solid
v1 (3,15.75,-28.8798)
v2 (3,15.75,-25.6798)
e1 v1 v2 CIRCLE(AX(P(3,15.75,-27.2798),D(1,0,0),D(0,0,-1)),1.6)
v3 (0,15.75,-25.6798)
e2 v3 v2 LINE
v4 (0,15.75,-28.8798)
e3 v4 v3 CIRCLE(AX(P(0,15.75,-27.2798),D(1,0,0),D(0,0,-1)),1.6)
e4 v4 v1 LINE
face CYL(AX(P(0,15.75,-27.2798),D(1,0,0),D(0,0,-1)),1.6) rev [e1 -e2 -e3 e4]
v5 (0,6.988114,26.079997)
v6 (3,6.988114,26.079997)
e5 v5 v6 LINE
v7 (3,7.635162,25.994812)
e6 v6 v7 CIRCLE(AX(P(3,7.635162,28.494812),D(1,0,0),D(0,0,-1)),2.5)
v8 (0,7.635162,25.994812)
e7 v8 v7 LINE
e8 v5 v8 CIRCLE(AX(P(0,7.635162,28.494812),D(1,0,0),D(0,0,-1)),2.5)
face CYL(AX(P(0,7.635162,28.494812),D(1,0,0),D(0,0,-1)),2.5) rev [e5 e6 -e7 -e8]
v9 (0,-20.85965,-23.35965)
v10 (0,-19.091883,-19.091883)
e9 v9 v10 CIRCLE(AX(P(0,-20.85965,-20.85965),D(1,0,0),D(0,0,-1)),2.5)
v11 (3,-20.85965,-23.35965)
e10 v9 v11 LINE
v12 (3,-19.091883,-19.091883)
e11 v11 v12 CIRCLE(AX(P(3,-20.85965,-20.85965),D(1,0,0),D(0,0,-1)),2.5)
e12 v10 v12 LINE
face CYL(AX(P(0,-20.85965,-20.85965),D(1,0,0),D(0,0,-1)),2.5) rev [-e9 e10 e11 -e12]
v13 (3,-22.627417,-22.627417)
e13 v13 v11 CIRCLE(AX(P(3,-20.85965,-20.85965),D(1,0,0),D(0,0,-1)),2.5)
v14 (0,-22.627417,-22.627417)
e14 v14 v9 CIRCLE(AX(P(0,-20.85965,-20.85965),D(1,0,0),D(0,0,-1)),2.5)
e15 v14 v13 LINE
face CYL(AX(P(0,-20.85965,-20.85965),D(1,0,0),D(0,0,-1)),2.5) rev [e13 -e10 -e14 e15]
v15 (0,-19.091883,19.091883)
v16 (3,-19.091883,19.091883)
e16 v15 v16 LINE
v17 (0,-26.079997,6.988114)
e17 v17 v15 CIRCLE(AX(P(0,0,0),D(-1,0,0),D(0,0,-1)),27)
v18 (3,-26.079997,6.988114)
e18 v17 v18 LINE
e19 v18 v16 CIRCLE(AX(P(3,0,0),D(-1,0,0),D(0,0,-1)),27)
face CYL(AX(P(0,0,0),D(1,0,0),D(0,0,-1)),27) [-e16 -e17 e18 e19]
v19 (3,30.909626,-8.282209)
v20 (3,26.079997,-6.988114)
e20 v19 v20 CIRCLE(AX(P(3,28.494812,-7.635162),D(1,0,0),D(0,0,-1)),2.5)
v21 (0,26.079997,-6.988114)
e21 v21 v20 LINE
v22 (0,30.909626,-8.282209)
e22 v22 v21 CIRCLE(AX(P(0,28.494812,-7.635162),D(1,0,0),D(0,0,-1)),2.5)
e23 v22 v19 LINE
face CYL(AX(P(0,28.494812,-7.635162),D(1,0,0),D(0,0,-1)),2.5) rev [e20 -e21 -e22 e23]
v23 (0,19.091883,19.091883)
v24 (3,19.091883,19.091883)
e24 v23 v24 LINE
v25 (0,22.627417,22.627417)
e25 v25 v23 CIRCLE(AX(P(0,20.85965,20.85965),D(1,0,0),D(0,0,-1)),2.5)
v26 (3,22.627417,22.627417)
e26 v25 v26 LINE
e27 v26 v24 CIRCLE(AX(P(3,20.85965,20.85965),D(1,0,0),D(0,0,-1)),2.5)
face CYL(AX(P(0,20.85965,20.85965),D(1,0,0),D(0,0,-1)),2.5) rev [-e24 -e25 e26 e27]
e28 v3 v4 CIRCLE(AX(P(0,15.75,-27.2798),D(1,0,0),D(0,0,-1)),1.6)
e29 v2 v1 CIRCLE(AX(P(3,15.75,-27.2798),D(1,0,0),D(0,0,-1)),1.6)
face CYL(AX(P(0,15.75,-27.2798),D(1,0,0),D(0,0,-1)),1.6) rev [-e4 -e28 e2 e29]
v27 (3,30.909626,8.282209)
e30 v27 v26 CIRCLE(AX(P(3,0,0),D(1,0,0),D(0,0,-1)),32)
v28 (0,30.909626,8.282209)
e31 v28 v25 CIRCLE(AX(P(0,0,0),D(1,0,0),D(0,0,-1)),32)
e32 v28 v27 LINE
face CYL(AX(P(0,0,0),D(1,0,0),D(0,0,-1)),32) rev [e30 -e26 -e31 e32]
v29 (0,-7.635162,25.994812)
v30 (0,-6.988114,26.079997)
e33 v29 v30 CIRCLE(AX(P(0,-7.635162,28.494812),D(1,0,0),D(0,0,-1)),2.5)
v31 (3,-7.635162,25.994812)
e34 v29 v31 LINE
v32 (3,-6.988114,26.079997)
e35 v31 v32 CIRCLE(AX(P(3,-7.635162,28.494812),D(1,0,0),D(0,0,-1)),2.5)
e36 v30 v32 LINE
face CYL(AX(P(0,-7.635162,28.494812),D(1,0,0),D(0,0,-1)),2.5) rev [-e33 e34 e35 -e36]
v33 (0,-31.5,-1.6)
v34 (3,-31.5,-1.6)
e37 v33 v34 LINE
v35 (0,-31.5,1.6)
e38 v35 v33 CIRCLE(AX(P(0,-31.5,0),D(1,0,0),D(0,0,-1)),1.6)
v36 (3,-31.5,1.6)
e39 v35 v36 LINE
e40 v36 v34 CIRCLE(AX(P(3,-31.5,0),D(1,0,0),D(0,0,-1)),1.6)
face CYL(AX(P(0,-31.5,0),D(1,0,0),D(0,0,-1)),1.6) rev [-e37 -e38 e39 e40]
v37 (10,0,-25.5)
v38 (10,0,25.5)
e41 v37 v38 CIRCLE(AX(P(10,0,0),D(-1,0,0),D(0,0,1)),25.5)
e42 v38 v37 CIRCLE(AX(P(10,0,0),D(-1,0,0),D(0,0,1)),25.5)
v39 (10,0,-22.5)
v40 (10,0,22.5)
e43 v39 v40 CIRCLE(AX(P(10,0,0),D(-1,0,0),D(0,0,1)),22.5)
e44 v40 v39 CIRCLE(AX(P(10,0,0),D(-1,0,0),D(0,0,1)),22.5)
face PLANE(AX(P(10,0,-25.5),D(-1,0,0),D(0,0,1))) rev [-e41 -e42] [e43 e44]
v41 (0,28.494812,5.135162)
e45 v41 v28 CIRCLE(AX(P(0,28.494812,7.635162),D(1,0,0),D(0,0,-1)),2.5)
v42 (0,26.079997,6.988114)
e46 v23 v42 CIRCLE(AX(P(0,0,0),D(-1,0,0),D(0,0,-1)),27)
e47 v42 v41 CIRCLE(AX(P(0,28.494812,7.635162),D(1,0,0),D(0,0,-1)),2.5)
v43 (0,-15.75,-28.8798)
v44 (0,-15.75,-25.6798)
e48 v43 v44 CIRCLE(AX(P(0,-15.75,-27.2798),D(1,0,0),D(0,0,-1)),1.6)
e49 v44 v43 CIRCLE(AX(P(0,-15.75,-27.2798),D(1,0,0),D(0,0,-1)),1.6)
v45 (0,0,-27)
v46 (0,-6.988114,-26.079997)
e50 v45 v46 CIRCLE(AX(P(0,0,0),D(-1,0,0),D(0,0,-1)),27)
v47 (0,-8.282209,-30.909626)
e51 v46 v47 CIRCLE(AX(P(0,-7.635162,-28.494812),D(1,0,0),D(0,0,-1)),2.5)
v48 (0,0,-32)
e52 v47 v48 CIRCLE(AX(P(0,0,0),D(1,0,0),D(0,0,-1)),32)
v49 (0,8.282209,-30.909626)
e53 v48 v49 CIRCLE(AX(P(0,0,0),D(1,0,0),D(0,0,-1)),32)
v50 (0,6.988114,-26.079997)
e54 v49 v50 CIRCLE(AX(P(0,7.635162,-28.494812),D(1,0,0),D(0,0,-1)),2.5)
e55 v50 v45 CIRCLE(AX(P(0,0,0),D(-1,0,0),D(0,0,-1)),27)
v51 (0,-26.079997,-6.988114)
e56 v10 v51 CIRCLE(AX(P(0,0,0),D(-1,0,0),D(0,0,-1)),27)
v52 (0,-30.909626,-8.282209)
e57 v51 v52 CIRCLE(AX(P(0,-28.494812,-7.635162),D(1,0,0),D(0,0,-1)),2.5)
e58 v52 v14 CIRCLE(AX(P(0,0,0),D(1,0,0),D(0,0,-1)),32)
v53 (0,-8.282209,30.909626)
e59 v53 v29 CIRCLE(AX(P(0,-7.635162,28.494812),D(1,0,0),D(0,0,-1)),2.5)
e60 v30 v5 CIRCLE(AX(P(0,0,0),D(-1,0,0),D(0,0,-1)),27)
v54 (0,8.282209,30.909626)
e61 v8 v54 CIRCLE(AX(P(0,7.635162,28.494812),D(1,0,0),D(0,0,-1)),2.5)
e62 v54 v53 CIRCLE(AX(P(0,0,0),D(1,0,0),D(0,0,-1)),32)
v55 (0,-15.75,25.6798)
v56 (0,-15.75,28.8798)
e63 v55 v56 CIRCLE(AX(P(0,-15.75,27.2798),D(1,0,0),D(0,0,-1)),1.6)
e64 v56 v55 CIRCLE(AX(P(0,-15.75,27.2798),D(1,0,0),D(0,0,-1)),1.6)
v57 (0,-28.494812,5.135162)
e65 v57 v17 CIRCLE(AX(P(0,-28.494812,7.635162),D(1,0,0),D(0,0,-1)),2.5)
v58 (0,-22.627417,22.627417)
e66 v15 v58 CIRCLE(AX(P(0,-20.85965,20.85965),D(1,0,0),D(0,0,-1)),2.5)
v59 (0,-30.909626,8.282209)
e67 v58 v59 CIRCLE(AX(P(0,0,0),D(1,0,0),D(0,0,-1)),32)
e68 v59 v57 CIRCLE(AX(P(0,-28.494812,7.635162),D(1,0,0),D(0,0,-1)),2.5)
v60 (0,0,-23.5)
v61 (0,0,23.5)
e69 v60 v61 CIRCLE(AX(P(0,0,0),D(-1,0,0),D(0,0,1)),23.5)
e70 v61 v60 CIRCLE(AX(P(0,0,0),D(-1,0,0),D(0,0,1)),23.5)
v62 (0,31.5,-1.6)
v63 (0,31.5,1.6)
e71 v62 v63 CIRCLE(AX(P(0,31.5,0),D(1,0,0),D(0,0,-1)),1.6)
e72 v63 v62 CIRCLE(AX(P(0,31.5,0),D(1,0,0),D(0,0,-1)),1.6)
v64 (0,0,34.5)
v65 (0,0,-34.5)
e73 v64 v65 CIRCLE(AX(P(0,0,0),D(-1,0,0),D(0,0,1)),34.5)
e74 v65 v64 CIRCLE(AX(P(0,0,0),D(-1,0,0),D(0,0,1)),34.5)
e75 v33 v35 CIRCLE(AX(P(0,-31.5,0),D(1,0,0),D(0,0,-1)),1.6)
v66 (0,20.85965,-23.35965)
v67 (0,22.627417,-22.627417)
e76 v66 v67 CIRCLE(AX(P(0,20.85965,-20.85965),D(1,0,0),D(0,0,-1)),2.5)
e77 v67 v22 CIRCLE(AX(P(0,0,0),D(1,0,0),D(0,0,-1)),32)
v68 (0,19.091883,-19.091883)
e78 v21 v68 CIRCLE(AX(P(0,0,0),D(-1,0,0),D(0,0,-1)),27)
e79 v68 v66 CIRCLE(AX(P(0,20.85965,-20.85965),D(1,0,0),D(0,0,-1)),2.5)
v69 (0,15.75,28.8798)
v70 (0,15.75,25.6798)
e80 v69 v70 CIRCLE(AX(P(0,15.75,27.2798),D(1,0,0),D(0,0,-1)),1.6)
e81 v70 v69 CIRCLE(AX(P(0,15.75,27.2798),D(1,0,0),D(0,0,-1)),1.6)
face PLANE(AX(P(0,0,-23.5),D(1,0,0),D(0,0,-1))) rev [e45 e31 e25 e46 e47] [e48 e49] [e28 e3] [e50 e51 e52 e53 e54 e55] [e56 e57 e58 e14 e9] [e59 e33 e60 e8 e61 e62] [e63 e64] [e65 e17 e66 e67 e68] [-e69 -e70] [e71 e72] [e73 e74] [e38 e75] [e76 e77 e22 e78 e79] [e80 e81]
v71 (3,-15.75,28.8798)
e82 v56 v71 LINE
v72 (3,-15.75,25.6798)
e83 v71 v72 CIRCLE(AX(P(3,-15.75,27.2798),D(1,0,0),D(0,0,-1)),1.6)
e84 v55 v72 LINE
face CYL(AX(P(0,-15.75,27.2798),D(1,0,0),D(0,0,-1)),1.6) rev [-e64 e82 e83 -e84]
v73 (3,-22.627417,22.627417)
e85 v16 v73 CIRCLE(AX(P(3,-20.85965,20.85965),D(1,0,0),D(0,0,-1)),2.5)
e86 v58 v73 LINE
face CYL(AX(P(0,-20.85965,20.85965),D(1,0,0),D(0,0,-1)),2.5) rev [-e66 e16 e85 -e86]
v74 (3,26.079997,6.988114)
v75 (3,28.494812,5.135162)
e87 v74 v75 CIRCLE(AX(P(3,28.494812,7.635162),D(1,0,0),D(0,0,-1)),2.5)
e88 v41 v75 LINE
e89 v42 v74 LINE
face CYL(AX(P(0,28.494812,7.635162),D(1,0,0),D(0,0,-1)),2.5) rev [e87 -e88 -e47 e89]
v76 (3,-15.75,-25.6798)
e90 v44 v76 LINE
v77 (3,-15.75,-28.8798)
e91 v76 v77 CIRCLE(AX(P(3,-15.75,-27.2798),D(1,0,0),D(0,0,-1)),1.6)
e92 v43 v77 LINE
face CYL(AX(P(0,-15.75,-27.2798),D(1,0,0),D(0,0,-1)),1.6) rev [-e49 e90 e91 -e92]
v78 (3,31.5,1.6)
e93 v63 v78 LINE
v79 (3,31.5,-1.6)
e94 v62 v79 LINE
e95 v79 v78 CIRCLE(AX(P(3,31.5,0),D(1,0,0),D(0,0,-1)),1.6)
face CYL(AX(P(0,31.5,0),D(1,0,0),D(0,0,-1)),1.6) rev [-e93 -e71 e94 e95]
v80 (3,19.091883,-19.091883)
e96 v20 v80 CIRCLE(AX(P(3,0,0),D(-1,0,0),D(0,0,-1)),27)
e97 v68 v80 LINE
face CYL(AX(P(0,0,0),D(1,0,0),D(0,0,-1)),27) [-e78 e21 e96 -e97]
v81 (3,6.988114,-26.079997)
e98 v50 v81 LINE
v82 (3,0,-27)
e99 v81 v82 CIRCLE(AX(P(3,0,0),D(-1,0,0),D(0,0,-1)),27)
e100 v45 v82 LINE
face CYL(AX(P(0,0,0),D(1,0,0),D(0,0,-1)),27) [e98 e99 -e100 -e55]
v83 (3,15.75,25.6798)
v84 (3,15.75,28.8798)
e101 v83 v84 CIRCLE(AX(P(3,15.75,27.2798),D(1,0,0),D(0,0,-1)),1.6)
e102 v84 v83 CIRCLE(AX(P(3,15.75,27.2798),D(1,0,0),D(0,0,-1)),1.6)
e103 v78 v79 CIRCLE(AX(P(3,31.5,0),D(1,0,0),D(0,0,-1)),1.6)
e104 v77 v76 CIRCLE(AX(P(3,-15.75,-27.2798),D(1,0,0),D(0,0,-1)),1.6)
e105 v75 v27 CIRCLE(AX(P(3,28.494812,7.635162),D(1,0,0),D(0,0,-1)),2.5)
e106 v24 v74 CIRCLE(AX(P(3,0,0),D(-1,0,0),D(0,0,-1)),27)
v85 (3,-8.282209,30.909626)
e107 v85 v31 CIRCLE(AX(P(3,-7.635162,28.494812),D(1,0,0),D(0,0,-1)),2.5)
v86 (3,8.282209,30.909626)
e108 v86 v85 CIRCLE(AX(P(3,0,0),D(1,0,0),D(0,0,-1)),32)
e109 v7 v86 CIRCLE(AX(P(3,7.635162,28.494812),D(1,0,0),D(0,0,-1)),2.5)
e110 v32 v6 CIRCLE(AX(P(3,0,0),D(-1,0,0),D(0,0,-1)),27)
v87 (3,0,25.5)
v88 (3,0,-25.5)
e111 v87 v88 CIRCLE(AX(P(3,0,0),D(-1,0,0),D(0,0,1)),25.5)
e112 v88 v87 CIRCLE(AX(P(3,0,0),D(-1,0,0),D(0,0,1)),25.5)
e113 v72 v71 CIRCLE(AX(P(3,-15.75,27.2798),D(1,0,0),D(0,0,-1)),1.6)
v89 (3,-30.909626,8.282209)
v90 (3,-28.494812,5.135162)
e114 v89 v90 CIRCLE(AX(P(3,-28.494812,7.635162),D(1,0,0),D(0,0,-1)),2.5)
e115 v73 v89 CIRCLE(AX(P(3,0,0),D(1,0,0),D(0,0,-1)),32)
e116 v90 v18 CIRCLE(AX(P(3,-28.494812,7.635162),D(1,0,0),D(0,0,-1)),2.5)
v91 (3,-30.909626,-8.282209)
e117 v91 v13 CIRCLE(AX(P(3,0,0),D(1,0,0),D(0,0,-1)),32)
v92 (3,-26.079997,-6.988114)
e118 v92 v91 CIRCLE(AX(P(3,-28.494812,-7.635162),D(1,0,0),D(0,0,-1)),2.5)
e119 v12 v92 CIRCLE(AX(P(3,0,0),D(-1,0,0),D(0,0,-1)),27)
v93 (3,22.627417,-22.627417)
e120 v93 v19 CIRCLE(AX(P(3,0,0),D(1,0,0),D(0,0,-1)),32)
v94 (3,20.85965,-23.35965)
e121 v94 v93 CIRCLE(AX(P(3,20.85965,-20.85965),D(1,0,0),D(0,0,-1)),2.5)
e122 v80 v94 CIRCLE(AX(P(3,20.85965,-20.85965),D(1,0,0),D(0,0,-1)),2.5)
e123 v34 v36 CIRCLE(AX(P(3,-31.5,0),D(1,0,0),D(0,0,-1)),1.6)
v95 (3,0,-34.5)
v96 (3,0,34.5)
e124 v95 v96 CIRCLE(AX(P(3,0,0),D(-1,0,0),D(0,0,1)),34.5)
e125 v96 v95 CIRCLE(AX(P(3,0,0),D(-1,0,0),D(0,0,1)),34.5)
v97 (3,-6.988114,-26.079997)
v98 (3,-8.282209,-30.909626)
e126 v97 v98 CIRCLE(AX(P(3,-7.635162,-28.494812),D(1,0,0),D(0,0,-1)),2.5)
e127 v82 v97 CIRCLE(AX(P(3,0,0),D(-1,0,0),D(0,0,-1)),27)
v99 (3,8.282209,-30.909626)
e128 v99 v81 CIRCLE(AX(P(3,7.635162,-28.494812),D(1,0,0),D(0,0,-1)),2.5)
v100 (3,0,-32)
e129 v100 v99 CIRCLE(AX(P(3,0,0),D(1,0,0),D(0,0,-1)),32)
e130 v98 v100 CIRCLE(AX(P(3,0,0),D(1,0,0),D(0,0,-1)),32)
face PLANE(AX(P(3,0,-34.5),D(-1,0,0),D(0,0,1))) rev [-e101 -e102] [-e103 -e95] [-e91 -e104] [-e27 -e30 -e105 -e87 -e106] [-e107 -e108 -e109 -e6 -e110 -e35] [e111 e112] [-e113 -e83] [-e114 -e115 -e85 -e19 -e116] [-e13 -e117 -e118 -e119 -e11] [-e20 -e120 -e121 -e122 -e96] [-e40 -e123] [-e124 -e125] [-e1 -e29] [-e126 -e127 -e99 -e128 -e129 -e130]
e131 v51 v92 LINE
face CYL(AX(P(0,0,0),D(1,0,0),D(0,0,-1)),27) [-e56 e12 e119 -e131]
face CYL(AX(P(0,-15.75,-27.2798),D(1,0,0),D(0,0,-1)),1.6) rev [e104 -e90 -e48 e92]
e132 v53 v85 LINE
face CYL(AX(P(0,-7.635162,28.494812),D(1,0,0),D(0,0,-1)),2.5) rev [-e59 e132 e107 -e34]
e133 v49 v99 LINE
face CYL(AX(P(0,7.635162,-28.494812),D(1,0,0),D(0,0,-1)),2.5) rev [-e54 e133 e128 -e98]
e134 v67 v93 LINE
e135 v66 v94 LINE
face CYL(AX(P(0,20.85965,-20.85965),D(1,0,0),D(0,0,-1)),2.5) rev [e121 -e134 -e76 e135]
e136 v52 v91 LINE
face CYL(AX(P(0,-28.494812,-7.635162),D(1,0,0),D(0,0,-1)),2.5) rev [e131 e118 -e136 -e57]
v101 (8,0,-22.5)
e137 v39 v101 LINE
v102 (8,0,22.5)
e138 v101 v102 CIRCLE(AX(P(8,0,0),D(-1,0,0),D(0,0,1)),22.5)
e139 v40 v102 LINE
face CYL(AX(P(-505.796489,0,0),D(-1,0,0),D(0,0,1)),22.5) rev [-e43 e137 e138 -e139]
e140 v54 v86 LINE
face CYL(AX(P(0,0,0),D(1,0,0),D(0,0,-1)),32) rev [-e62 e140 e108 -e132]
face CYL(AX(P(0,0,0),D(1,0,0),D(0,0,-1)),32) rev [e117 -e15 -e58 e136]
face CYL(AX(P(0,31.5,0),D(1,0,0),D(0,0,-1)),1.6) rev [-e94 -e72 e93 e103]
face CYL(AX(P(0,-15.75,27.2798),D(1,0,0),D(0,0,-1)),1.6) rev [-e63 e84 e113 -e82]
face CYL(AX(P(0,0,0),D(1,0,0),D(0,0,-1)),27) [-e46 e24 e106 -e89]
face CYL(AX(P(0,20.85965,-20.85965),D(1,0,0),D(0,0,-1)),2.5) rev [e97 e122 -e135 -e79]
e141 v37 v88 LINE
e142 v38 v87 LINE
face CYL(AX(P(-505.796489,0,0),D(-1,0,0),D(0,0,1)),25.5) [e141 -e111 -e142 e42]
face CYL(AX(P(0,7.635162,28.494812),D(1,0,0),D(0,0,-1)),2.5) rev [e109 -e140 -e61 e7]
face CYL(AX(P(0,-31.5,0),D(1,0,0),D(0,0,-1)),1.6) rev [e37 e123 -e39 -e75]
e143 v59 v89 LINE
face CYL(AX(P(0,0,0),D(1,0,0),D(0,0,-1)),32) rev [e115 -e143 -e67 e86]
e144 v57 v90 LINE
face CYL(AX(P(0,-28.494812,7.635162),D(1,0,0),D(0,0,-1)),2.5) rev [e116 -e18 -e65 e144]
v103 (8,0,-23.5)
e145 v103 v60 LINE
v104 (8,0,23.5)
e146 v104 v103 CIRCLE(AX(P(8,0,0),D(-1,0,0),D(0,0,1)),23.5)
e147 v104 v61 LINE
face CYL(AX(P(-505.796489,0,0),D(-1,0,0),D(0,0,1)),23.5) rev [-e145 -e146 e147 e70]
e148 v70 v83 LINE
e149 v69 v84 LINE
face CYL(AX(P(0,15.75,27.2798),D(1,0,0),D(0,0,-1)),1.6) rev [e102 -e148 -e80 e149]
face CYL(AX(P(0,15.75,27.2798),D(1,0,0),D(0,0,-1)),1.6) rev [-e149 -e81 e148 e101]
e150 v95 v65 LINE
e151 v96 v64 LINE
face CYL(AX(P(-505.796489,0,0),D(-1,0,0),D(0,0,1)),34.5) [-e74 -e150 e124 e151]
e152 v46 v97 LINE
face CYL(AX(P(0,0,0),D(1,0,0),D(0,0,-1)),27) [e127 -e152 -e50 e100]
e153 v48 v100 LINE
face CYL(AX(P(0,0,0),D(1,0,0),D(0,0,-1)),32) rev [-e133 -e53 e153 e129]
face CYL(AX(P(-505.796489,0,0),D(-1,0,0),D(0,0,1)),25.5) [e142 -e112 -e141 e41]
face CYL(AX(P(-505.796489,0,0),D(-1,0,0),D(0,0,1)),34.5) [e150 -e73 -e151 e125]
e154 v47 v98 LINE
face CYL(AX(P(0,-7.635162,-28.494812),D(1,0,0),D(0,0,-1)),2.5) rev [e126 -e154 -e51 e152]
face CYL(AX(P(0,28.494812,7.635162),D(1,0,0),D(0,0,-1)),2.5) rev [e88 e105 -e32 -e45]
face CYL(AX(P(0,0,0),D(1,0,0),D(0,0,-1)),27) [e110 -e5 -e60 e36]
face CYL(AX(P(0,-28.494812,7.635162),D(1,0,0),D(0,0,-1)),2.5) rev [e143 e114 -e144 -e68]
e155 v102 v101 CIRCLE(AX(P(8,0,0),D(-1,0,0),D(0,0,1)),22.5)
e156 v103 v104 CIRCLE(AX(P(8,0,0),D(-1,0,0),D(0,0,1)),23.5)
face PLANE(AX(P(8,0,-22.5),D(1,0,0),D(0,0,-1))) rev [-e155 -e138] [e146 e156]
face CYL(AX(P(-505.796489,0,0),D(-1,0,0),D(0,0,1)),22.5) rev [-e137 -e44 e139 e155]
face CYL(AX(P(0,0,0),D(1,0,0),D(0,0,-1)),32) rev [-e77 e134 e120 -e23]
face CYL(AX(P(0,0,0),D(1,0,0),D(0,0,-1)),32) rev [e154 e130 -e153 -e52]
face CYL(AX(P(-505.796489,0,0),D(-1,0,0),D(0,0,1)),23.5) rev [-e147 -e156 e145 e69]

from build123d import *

# Parameters (mm, degrees)
SKETCH_2_R          = 1.6
CUT_EXTRUDE_1_DEPTH = 50.289958409
CUT_EXTRUDE_2_DEPTH = 50.289958409


with BuildPart() as part:
    # 草图1 → 旋转1 (revolve)
    with BuildSketch(Plane(origin=(0, 0, 0), x_dir=(1, 0, 0), z_dir=(0, 1, 0)), mode=Mode.PRIVATE) as revolve_1_sk:
        Polygon((0, 23.5), (0, 34.5), (3, 34.5), (3, 25.5), (10, 25.5), (10, 22.5), (8, 22.5), (8, 23.5), align=None)
    revolve(revolve_1_sk.sketch.rotate(Axis((-505.796489034, 0, 0), (1, 0, 0)), 180), axis=Axis((-505.796489034, 0, 0), (1, 0, 0)))

    # 草图2 → 切除-拉伸1 (cut, through all)
    with BuildSketch(Plane(origin=(3, 0, 0), x_dir=(0, 0, -1), z_dir=(1, 0, 0))):
        with Locations((0, 31.5)):
            Circle(SKETCH_2_R)
        with Locations((27.279800219, 15.75)):
            Circle(SKETCH_2_R)
        with Locations((27.279800219, -15.75)):
            Circle(SKETCH_2_R)
        with Locations((0, -31.5)):
            Circle(SKETCH_2_R)
        with Locations((-27.279800219, -15.75)):
            Circle(SKETCH_2_R)
        with Locations((-27.279800219, 15.75)):
            Circle(SKETCH_2_R)
    extrude(amount=-CUT_EXTRUDE_1_DEPTH, mode=Mode.SUBTRACT)

    # 草图3 → 切除-拉伸2 (cut, through all)
    with BuildSketch(Plane(origin=(3, 0, 0), x_dir=(0, 0, -1), z_dir=(1, 0, 0))):
        with BuildLine():
            ThreePointArc((22.627416998, 22.627416998), (16, 27.712812921), (8.282209443, 30.909626441))
            ThreePointArc((8.282209443, 30.909626441), (5.220347265, 29.141859488), (6.988114218, 26.07999731))
            ThreePointArc((6.988114218, 26.07999731), (13.5, 23.382685902), (19.091883092, 19.091883092))
            ThreePointArc((19.091883092, 19.091883092), (22.627416998, 19.091883092), (22.627416998, 22.627416998))
        make_face()
        with BuildLine():
            ThreePointArc((30.909626441, -8.282209443), (32, 0), (30.909626441, 8.282209443))
            ThreePointArc((30.909626441, 8.282209443), (27.847764263, 10.049976396), (26.07999731, 6.988114218))
            ThreePointArc((26.07999731, 6.988114218), (27, 0), (26.07999731, -6.988114218))
            ThreePointArc((26.07999731, -6.988114218), (27.847764263, -10.049976396), (30.909626441, -8.282209443))
        make_face()
        with BuildLine():
            ThreePointArc((8.282209443, -30.909626441), (16, -27.712812921), (22.627416998, -22.627416998))
            ThreePointArc((22.627416998, -22.627416998), (22.627416998, -19.091883092), (19.091883092, -19.091883092))
            ThreePointArc((19.091883092, -19.091883092), (13.5, -23.382685902), (6.988114218, -26.07999731))
            ThreePointArc((6.988114218, -26.07999731), (5.220347265, -29.141859488), (8.282209443, -30.909626441))
        make_face()
        with BuildLine():
            ThreePointArc((-22.627416998, -22.627416998), (-16, -27.712812921), (-8.282209443, -30.909626441))
            ThreePointArc((-8.282209443, -30.909626441), (-5.220347265, -29.141859488), (-6.988114218, -26.07999731))
            ThreePointArc((-6.988114218, -26.07999731), (-13.5, -23.382685902), (-19.091883092, -19.091883092))
            ThreePointArc((-19.091883092, -19.091883092), (-22.627416998, -19.091883092), (-22.627416998, -22.627416998))
        make_face()
        with BuildLine():
            ThreePointArc((-30.909626441, 8.282209443), (-32, 0), (-30.909626441, -8.282209443))
            ThreePointArc((-30.909626441, -8.282209443), (-27.847764263, -10.049976396), (-26.07999731, -6.988114218))
            ThreePointArc((-26.07999731, -6.988114218), (-27, 0), (-26.07999731, 6.988114218))
            ThreePointArc((-26.07999731, 6.988114218), (-27.847764263, 10.049976396), (-30.909626441, 8.282209443))
        make_face()
        with BuildLine():
            ThreePointArc((-8.282209443, 30.909626441), (-16, 27.712812921), (-22.627416998, 22.627416998))
            ThreePointArc((-22.627416998, 22.627416998), (-22.627416998, 19.091883092), (-19.091883092, 19.091883092))
            ThreePointArc((-19.091883092, 19.091883092), (-13.5, 23.382685902), (-6.988114218, 26.07999731))
            ThreePointArc((-6.988114218, 26.07999731), (-5.220347265, 29.141859488), (-8.282209443, 30.909626441))
        make_face()
    extrude(amount=-CUT_EXTRUDE_2_DEPTH, mode=Mode.SUBTRACT)


solid = part.part
